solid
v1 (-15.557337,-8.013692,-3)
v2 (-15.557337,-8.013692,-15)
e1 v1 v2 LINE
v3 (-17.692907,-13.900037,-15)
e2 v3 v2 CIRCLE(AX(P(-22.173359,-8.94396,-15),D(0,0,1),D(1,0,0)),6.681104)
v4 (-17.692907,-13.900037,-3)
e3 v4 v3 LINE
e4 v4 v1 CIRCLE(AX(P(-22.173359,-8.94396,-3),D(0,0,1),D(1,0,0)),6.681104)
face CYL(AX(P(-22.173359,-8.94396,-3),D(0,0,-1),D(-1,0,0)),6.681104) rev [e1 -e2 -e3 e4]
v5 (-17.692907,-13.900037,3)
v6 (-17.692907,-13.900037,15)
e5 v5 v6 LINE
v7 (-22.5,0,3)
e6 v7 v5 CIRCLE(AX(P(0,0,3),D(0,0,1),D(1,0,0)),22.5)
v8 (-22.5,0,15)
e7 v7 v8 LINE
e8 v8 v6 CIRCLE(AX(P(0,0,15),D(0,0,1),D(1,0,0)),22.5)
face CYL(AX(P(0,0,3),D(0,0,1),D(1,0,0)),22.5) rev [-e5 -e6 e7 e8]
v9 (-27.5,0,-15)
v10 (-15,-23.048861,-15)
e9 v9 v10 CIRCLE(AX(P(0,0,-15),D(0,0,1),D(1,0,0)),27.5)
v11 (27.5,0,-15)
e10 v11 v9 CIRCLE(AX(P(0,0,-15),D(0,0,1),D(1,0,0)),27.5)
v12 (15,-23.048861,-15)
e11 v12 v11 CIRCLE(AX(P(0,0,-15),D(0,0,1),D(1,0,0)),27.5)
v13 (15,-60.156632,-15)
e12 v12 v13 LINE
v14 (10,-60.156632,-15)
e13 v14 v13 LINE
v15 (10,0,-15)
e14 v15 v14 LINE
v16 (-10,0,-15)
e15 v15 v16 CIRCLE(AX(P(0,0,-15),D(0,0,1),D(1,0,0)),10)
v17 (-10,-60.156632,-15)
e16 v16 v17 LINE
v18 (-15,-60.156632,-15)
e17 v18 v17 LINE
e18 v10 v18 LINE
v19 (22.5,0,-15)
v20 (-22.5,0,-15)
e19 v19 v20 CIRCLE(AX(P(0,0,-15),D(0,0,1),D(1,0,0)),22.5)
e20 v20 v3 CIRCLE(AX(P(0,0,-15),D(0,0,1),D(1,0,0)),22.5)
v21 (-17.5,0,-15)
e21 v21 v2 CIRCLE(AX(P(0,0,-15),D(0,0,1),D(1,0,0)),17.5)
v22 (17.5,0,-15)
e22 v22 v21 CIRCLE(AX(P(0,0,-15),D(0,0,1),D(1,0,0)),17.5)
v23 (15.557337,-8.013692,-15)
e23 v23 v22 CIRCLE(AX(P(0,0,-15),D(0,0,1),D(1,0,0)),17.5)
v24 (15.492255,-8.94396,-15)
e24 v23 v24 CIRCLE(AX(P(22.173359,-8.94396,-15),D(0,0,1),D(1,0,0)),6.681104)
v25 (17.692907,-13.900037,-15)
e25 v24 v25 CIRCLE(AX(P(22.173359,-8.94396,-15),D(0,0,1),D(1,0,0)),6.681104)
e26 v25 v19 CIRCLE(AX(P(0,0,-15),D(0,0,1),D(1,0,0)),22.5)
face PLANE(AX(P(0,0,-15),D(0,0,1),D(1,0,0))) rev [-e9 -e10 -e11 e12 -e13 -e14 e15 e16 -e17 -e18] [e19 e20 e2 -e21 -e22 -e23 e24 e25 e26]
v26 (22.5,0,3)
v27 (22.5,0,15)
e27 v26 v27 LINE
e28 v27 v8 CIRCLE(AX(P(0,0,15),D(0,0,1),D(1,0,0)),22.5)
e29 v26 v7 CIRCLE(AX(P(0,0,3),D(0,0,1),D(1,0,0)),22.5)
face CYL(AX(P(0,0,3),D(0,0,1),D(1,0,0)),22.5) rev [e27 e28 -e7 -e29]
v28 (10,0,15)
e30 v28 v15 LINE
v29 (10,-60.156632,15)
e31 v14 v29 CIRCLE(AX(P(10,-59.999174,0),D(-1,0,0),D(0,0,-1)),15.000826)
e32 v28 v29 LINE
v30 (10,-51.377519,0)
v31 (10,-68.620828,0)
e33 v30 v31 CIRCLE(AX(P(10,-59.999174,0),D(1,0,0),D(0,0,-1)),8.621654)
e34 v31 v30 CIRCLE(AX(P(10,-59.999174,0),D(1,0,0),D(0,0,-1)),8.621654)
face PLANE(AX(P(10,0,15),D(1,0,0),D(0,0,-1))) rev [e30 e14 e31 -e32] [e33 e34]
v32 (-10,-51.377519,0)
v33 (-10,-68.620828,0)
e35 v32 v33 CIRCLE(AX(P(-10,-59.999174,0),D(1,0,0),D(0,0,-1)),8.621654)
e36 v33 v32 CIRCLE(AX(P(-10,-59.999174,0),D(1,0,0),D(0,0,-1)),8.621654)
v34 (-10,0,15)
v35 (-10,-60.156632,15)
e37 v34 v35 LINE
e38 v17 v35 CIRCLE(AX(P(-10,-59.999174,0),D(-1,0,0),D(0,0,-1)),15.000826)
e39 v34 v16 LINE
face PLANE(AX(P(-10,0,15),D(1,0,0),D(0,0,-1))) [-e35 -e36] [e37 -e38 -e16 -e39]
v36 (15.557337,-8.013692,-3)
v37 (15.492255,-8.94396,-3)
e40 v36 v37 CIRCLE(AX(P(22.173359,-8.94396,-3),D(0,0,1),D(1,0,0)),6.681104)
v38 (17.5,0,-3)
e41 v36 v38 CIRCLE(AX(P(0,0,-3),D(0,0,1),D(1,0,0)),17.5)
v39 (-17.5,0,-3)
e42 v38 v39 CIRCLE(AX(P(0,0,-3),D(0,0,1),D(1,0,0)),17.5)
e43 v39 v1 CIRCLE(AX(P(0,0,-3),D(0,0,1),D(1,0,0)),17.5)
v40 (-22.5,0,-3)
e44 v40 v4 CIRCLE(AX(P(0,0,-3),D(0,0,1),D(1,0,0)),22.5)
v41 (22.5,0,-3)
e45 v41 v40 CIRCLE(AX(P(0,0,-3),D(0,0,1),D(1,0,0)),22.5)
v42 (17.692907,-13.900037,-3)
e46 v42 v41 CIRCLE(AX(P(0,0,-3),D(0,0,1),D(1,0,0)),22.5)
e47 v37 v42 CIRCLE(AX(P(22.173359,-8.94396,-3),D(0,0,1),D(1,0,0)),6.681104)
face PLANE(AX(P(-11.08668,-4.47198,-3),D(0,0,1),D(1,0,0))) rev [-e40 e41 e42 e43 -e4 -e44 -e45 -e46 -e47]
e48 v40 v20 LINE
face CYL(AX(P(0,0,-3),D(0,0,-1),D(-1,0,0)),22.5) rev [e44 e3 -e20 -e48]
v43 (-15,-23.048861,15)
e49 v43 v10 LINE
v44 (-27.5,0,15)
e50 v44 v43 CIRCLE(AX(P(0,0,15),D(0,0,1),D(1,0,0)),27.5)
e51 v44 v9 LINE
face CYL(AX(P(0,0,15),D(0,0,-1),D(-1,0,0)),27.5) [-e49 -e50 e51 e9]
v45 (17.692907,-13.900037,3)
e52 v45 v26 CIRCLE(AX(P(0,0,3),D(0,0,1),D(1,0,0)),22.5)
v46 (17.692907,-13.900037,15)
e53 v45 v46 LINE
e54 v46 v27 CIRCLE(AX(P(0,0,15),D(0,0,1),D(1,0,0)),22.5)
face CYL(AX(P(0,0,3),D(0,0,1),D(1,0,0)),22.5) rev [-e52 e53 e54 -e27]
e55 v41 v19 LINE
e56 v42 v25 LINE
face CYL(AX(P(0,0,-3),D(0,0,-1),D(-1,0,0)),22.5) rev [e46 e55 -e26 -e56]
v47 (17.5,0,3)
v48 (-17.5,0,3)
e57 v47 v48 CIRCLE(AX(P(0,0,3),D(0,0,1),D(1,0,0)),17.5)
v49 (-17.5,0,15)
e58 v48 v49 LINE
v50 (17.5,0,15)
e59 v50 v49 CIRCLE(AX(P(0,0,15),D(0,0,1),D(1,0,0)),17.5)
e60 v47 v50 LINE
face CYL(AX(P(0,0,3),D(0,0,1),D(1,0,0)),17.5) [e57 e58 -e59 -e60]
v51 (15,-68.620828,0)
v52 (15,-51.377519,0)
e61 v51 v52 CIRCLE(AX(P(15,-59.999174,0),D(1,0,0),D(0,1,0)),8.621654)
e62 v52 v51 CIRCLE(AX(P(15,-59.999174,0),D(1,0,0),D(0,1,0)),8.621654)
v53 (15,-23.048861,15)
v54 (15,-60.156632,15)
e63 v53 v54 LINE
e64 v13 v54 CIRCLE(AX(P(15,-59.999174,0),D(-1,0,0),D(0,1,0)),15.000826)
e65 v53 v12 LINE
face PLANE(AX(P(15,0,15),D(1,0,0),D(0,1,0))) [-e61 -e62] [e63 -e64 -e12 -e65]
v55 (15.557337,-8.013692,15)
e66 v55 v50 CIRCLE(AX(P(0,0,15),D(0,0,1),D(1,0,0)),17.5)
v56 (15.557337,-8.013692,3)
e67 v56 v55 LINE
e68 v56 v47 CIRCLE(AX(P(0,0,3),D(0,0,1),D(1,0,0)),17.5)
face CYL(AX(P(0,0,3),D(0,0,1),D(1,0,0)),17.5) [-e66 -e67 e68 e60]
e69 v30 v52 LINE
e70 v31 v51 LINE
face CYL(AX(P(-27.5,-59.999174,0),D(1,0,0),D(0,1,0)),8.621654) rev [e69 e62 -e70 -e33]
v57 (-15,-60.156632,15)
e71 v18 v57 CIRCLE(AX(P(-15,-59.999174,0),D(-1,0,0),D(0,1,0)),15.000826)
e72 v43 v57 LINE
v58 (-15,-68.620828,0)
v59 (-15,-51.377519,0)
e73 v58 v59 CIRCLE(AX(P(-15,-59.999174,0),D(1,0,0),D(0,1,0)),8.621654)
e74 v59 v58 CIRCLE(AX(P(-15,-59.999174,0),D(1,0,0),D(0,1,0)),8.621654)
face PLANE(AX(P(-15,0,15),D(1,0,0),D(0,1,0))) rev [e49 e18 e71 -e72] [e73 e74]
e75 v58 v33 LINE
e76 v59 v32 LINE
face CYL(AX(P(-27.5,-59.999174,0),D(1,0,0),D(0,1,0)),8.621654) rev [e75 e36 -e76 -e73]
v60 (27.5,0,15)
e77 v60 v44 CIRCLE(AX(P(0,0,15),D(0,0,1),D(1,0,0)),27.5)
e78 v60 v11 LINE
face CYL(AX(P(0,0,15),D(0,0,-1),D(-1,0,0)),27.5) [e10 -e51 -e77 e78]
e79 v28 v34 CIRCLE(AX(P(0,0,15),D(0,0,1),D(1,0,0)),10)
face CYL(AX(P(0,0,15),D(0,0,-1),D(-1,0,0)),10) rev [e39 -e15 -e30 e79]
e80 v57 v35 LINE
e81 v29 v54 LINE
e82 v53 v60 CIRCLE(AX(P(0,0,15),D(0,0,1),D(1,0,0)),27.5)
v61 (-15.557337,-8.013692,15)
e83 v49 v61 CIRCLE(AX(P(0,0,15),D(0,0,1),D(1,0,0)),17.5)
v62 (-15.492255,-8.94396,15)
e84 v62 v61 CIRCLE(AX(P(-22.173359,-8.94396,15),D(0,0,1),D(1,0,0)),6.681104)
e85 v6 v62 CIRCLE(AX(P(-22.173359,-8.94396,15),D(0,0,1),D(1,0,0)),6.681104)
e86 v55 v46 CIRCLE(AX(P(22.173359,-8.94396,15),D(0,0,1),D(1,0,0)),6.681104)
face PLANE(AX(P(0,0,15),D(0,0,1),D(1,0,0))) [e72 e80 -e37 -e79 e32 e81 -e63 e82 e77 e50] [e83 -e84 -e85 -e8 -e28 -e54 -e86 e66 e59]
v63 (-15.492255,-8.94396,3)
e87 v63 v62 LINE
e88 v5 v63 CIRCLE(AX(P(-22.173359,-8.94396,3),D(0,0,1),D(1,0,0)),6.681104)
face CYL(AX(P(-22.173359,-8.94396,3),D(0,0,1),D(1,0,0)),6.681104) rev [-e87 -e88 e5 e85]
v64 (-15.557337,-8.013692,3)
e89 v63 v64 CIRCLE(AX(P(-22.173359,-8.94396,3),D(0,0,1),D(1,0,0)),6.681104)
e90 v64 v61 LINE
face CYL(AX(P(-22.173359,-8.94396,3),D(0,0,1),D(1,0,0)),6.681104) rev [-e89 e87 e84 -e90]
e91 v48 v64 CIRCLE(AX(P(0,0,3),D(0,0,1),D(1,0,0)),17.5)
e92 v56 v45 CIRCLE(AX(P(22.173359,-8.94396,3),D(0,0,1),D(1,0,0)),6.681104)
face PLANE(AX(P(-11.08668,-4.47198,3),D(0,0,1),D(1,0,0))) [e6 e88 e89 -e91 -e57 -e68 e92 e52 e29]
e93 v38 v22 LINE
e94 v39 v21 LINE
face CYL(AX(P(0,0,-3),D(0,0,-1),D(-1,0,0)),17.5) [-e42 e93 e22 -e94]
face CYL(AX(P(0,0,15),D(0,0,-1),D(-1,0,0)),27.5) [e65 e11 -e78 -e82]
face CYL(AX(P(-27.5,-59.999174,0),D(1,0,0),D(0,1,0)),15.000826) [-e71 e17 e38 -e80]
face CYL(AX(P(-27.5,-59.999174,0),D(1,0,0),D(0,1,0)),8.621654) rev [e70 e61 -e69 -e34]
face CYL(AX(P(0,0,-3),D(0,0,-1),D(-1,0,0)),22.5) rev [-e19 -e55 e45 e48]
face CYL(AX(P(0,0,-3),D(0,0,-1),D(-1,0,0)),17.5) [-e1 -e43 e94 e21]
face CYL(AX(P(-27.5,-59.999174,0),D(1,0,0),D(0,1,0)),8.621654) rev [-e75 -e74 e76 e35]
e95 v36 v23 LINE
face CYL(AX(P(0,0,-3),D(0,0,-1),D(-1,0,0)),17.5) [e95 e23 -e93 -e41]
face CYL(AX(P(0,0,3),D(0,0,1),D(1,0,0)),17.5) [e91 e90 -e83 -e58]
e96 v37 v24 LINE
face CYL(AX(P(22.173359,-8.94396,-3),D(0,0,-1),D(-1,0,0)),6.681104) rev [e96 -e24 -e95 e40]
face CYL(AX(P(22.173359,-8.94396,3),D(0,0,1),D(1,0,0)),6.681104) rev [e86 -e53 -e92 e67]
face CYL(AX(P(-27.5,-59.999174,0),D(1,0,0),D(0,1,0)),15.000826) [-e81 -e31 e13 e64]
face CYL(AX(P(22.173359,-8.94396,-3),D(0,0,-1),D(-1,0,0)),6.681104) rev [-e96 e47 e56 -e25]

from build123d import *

# Parameters (mm, degrees)
CLEVIS_BODY_DEPTH        = 15
PROFILE_START            = 15
PROFILE_CUT_A_12MM_DEPTH = 12
PROFILE_START_2          = -15
PROFILE_CUT_B_12MM_DEPTH = 12
HEAD_SLOT_SKETCH_R       = 8.62165443
HEAD_SLOT_CUT_DEPTH      = 88.5


with BuildPart() as part:
    # Clevis Profile Sketch → Clevis Body (new, symmetric)
    # profile 1 of 3: a face of its own
    with BuildSketch(Plane.XY):
        with BuildLine():
            ThreePointArc((-15, 0), (0, 15), (15, 0))
            Line((15, 0), (15, -23.048861143))
            ThreePointArc((15, -23.048861143), (0, 27.5), (-15, -23.048861143))
            Line((-15, -23.048861143), (-15, 0))
        make_face()
        with BuildLine():
            ThreePointArc((-17.692907365, -13.900037013), (0, 22.5), (17.692907365, -13.900037013))
            ThreePointArc((17.692907365, -13.900037013), (15.892818017, -11.22254507), (15.557337138, -8.013692106))
            ThreePointArc((15.557337138, -8.013692106), (0, 17.5), (-15.557337138, -8.013692106))
            ThreePointArc((-15.557337138, -8.013692106), (-15.892818017, -11.22254507), (-17.692907365, -13.900037013))
        make_face(mode=Mode.SUBTRACT)
    # profile 2 of 3: a face of its own
    with BuildSketch(Plane.XY):
        with BuildLine():
            ThreePointArc((17.692907365, -13.900037013), (15.892818017, -11.22254507), (15.557337138, -8.013692106))
            ThreePointArc((15.557337138, -8.013692106), (0, 17.5), (-15.557337138, -8.013692106))
            ThreePointArc((-15.557337138, -8.013692106), (-15.892818017, -11.22254507), (-17.692907365, -13.900037013))
            ThreePointArc((-17.692907365, -13.900037013), (0, 22.5), (17.692907365, -13.900037013))
        make_face()
    # profile 3 of 3: a face of its own
    with BuildSketch(Plane.XY):
        with BuildLine():
            ThreePointArc((10, 0), (0, 10), (-10, 0))
            Line((-10, 0), (-10, -75))
            Line((-10, -75), (-15, -75))
            Line((-15, -75), (-15, 0))
            ThreePointArc((-15, 0), (0, 15), (15, 0))
            Line((15, 0), (15, -75))
            Line((15, -75), (10, -75))
            Line((10, -75), (10, 0))
        make_face()
    extrude(amount=CLEVIS_BODY_DEPTH, both=True)

    # Sketch1_3 → Profile Cut A 12mm (cut)
    with BuildSketch(Plane.XY.offset(PROFILE_START)):
        with BuildLine():
            ThreePointArc((17.692907365, -13.900037013), (15.892818017, -11.22254507), (15.557337138, -8.013692106))
            ThreePointArc((15.557337138, -8.013692106), (0, 17.5), (-15.557337138, -8.013692106))
            ThreePointArc((-15.557337138, -8.013692106), (-15.892818017, -11.22254507), (-17.692907365, -13.900037013))
            ThreePointArc((-17.692907365, -13.900037013), (0, 22.5), (17.692907365, -13.900037013))
        make_face()
    extrude(amount=-PROFILE_CUT_A_12MM_DEPTH, mode=Mode.SUBTRACT)

    # Sketch1_4 → Profile Cut B 12mm (cut)
    with BuildSketch(Plane.XY.offset(PROFILE_START_2)):
        with BuildLine():
            ThreePointArc((17.692907365, -13.900037013), (15.892818017, -11.22254507), (15.557337138, -8.013692106))
            ThreePointArc((15.557337138, -8.013692106), (0, 17.5), (-15.557337138, -8.013692106))
            ThreePointArc((-15.557337138, -8.013692106), (-15.892818017, -11.22254507), (-17.692907365, -13.900037013))
            ThreePointArc((-17.692907365, -13.900037013), (0, 22.5), (17.692907365, -13.900037013))
        make_face()
    extrude(amount=PROFILE_CUT_B_12MM_DEPTH, mode=Mode.SUBTRACT)

    # Head Slot Sketch → Head Slot Cut (cut, through all)
    with BuildSketch(Plane(origin=(15, 0, 0), x_dir=(0, 0, -1), z_dir=(1, 0, 0))):
        with Locations(Location((0, -59.999173584, 0), (0, 0, 90))):
            Circle(HEAD_SLOT_SKETCH_R)
        with BuildLine():
            Line((-15, -75), (0, -75))
            ThreePointArc((0, -75), (-10.55136927, -70.661884294), (-15, -60.15663199))
            Line((-15, -60.15663199), (-15, -75))
        make_face()
        with BuildLine():
            Line((15, -75), (15, -60.15663199))
            ThreePointArc((15, -60.15663199), (10.55136927, -70.661884294), (0, -75))
            Line((0, -75), (15, -75))
        make_face()
    extrude(amount=-HEAD_SLOT_CUT_DEPTH, mode=Mode.SUBTRACT)


solid = part.part
